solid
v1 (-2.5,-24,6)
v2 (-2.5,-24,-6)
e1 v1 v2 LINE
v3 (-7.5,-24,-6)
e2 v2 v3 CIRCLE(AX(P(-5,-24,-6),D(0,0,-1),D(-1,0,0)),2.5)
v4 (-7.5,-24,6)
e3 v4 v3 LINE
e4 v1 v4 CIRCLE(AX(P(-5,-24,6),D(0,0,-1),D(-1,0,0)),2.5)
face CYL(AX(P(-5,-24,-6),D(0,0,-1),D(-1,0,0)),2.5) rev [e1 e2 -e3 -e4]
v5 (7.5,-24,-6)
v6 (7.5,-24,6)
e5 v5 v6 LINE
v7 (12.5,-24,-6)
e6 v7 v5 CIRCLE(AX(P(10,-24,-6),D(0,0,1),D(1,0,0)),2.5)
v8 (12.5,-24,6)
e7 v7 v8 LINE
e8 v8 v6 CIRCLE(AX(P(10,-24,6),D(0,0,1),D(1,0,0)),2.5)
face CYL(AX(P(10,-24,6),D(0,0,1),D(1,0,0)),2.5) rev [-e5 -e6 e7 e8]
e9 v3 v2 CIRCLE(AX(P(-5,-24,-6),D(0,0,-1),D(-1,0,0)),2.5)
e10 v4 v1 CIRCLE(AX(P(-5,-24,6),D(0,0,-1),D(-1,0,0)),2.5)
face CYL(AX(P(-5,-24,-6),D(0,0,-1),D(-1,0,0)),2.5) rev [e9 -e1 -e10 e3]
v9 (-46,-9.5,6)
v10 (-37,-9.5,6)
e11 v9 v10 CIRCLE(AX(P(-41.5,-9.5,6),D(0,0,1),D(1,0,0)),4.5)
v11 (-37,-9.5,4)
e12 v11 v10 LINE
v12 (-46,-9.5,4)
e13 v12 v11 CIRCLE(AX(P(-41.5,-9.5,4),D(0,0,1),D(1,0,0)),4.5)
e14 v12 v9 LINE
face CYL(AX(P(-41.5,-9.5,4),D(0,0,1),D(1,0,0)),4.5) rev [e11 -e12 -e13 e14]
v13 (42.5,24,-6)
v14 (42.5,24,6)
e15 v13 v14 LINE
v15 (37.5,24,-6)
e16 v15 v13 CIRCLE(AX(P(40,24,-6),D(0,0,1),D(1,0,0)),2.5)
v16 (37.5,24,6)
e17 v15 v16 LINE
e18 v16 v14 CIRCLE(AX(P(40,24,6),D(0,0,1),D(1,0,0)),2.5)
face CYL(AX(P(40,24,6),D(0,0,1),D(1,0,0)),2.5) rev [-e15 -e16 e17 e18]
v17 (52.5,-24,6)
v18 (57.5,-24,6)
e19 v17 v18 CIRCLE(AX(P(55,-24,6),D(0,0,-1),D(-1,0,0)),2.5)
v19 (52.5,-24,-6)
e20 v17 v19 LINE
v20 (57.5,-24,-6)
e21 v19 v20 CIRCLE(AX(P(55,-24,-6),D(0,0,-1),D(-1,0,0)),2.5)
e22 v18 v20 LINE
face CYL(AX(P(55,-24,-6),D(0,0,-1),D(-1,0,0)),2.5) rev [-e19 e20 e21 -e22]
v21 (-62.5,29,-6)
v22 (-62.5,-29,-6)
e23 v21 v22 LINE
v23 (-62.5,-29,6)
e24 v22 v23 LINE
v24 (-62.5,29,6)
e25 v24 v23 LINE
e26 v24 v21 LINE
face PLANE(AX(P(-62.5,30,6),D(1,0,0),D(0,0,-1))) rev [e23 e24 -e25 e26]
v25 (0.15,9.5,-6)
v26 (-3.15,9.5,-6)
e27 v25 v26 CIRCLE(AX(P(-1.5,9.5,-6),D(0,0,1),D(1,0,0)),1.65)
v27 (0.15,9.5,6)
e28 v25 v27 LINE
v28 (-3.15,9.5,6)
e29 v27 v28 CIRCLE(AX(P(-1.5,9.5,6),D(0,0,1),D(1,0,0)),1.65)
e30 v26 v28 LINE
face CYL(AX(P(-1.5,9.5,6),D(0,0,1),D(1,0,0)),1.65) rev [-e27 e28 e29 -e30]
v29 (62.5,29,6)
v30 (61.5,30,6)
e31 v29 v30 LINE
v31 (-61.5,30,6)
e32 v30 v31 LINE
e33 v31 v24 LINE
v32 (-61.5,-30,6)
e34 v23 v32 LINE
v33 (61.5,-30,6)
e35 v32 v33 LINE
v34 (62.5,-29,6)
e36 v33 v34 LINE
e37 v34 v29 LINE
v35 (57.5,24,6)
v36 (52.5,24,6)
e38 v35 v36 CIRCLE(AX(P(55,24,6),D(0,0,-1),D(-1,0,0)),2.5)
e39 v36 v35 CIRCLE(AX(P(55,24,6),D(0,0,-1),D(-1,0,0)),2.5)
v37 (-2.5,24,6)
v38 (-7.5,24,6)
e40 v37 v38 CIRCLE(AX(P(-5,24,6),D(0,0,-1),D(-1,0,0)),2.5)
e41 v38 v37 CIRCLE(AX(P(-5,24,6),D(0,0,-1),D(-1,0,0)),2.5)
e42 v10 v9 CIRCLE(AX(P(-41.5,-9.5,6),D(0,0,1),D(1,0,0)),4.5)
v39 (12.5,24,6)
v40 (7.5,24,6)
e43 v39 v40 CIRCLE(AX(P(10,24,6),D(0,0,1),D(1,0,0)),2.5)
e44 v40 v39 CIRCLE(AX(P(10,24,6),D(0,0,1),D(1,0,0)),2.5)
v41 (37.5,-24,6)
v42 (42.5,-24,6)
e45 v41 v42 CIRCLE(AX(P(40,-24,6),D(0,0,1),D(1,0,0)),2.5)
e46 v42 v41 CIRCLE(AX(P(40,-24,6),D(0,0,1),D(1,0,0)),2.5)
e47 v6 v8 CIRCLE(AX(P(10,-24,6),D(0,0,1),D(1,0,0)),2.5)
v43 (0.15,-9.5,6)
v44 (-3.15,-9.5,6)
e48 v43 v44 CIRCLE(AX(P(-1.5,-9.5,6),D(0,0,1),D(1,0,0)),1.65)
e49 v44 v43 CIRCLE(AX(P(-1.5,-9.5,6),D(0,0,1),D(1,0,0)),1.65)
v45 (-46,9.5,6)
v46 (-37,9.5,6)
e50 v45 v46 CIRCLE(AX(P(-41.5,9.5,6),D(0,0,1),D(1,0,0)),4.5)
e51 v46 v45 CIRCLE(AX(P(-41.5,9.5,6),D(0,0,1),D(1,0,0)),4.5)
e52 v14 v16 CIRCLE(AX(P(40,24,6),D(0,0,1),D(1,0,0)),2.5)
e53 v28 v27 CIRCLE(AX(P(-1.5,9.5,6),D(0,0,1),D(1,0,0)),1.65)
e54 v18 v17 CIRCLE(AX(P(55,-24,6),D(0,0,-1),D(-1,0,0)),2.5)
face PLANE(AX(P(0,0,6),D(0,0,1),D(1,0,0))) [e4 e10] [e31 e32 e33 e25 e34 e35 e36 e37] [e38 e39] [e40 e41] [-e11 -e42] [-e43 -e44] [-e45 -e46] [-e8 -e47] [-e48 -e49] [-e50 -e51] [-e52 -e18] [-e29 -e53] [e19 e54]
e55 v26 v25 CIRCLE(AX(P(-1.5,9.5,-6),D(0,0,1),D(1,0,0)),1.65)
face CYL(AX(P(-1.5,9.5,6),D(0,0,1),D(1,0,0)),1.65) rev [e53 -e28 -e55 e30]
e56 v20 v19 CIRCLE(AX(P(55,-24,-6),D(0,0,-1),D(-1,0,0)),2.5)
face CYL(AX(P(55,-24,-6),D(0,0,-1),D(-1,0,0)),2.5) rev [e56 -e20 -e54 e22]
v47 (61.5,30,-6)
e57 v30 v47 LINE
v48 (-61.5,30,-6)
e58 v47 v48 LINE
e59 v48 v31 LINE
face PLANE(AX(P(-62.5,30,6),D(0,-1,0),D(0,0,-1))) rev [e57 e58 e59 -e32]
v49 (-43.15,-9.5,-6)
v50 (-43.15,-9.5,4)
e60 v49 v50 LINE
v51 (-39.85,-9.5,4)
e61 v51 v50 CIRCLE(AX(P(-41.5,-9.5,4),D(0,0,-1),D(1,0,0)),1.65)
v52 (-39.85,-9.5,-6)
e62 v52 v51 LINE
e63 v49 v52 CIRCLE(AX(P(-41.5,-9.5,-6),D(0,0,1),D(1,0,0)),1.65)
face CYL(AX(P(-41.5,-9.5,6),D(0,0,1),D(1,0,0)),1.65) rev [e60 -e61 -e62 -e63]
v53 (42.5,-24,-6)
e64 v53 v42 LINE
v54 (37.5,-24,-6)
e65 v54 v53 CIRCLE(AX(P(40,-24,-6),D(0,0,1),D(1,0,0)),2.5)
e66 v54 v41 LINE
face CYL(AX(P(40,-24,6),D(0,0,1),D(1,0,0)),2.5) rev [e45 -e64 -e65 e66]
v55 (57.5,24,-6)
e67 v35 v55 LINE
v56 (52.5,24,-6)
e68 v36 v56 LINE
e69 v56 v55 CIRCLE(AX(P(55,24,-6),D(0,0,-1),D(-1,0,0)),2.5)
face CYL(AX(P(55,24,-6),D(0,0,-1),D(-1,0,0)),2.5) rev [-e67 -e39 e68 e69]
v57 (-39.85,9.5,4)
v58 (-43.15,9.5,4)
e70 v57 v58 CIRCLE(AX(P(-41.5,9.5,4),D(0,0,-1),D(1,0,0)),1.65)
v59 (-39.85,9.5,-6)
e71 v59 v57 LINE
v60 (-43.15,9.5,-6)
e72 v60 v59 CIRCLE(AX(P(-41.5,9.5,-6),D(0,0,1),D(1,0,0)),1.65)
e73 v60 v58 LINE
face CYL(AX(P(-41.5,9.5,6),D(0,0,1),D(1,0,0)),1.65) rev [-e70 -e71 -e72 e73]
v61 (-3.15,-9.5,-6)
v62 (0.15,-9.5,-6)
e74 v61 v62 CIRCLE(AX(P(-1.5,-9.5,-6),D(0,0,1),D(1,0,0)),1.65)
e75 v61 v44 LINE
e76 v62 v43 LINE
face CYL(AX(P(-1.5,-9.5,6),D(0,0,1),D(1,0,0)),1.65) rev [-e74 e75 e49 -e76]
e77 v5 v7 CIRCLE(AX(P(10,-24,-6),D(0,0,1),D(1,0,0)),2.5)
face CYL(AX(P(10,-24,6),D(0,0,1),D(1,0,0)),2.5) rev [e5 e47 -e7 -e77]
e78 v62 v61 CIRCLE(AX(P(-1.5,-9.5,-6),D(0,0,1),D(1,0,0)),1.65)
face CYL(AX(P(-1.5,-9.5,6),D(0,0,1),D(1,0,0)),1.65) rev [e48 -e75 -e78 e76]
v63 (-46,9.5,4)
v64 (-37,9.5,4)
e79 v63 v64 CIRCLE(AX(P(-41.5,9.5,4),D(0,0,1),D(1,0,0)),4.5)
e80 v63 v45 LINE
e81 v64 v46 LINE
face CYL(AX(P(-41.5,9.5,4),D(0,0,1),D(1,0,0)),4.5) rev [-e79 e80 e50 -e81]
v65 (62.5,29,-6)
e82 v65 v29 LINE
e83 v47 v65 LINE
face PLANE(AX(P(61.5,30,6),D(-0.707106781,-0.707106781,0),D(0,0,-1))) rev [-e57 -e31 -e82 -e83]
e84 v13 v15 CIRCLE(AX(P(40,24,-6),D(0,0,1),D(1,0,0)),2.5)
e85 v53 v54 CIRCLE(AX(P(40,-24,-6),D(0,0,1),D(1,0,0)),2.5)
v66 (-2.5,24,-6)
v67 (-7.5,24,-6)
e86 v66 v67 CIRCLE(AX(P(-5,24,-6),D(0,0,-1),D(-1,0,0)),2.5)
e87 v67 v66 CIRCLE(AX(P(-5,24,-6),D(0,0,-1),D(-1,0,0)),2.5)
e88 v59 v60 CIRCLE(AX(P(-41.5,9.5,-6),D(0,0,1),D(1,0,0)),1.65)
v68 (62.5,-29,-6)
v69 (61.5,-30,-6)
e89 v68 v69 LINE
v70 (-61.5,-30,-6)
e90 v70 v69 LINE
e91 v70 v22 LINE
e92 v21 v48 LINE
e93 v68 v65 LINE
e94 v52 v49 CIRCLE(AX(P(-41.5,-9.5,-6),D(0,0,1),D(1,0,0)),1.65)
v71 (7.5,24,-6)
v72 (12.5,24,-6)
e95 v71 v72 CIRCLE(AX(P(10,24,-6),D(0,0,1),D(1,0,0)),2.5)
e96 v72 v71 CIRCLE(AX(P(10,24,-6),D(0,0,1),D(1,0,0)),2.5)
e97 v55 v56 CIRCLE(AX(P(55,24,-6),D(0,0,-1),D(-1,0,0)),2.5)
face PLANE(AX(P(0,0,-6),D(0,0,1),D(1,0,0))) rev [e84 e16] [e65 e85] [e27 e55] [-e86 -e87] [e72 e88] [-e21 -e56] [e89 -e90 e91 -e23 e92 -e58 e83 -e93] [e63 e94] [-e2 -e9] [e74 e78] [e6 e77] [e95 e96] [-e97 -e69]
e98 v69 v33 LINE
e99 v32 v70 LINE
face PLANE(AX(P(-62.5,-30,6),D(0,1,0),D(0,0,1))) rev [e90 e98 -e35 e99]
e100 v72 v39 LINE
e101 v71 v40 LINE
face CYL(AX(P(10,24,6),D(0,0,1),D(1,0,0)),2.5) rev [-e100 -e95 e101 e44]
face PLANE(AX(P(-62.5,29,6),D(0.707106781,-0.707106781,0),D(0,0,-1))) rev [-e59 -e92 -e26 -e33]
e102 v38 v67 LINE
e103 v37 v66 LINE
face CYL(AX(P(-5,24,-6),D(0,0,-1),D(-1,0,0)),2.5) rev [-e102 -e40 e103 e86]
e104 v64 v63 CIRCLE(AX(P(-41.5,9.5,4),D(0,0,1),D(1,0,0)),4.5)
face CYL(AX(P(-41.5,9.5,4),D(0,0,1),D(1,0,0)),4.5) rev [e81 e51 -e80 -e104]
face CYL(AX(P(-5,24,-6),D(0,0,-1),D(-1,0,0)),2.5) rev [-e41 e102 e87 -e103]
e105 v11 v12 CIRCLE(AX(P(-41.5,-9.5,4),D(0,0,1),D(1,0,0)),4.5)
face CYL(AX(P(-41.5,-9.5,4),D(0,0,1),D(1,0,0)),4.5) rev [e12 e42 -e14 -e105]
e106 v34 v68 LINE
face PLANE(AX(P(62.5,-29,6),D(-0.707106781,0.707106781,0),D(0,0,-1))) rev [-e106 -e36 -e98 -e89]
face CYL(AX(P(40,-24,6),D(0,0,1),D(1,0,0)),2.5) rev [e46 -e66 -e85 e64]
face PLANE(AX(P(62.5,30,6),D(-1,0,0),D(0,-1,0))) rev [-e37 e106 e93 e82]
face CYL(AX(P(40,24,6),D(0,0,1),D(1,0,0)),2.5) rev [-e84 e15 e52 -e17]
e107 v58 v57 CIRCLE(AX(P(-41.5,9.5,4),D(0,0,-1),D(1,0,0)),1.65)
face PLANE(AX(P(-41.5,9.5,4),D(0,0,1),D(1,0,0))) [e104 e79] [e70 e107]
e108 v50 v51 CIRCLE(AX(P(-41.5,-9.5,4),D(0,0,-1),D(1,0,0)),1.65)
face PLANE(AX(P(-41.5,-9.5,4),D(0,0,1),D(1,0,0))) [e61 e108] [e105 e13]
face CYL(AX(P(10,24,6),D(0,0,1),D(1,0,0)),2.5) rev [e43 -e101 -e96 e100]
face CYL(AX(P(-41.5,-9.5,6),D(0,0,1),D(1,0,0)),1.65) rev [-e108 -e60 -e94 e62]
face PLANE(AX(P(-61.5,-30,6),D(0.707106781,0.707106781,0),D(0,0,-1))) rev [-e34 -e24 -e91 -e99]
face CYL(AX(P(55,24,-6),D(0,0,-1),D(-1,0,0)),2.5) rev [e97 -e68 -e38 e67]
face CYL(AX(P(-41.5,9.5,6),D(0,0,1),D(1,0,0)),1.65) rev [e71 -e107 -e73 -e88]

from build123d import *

# Parameters (mm, degrees)
SKETCH1_W                 = 125
SKETCH1_H                 = 60
BOSS_EXTRUDE1_DEPTH       = 6
M6_TAPPED_HOLE1_D         = 5
M4_TAPPED_HOLE1_D         = 3.3
SKETCH8_R                 = 4.5
CUT_EXTRUDE1_DEPTH        = 2
BLIND_PIN_HOLE1_SIZE_MM_D = 5
CHAMFER1_SIZE             = 1


with BuildPart() as part:
    # Sketch1 → Boss-Extrude1 (new, symmetric)
    with BuildSketch(Plane.XY):
        Rectangle(SKETCH1_W, SKETCH1_H)
    extrude(amount=BOSS_EXTRUDE1_DEPTH, both=True)

    # M6 Tapped Hole1 (through all)
    with Locations(Plane(origin=(0, 0, -6), x_dir=(-1, 0, 0), z_dir=(0, 0, -1))):
        with Locations((5, 24), (5, -24), (-55, -24), (-55, 24)):
            Hole(M6_TAPPED_HOLE1_D / 2)

    # M4 Tapped Hole1 (through all)
    with Locations(Plane.XY.offset(6)):
        with Locations((-1.5, 9.5), (-1.5, -9.5), (-41.5, -9.5), (-41.5, 9.5)):
            Hole(M4_TAPPED_HOLE1_D / 2)

    # Sketch8 → Cut-Extrude1 (cut)
    with BuildSketch(Plane.XY.offset(6)):
        with Locations((-41.5, 9.5)):
            Circle(SKETCH8_R)
        with Locations((-41.5, -9.5)):
            Circle(SKETCH8_R)
    extrude(amount=-CUT_EXTRUDE1_DEPTH, mode=Mode.SUBTRACT)

    # Blind Pin Hole1 (size mm) (through all)
    with Locations(Plane.XY.offset(6)):
        with Locations((10, 24), (40, 24), (10, -24), (40, -24)):
            Hole(BLIND_PIN_HOLE1_SIZE_MM_D / 2)

    # Chamfer1
    chamfer1_edges = [part.edges().sort_by_distance(p)[0] for p in [
        (62.5, -30, 0),
        (-62.5, -30, 0),
        (-62.5, 30, 0),
        (62.5, 30, 0),
    ]]
    chamfer(chamfer1_edges, length=CHAMFER1_SIZE)


solid = part.part
